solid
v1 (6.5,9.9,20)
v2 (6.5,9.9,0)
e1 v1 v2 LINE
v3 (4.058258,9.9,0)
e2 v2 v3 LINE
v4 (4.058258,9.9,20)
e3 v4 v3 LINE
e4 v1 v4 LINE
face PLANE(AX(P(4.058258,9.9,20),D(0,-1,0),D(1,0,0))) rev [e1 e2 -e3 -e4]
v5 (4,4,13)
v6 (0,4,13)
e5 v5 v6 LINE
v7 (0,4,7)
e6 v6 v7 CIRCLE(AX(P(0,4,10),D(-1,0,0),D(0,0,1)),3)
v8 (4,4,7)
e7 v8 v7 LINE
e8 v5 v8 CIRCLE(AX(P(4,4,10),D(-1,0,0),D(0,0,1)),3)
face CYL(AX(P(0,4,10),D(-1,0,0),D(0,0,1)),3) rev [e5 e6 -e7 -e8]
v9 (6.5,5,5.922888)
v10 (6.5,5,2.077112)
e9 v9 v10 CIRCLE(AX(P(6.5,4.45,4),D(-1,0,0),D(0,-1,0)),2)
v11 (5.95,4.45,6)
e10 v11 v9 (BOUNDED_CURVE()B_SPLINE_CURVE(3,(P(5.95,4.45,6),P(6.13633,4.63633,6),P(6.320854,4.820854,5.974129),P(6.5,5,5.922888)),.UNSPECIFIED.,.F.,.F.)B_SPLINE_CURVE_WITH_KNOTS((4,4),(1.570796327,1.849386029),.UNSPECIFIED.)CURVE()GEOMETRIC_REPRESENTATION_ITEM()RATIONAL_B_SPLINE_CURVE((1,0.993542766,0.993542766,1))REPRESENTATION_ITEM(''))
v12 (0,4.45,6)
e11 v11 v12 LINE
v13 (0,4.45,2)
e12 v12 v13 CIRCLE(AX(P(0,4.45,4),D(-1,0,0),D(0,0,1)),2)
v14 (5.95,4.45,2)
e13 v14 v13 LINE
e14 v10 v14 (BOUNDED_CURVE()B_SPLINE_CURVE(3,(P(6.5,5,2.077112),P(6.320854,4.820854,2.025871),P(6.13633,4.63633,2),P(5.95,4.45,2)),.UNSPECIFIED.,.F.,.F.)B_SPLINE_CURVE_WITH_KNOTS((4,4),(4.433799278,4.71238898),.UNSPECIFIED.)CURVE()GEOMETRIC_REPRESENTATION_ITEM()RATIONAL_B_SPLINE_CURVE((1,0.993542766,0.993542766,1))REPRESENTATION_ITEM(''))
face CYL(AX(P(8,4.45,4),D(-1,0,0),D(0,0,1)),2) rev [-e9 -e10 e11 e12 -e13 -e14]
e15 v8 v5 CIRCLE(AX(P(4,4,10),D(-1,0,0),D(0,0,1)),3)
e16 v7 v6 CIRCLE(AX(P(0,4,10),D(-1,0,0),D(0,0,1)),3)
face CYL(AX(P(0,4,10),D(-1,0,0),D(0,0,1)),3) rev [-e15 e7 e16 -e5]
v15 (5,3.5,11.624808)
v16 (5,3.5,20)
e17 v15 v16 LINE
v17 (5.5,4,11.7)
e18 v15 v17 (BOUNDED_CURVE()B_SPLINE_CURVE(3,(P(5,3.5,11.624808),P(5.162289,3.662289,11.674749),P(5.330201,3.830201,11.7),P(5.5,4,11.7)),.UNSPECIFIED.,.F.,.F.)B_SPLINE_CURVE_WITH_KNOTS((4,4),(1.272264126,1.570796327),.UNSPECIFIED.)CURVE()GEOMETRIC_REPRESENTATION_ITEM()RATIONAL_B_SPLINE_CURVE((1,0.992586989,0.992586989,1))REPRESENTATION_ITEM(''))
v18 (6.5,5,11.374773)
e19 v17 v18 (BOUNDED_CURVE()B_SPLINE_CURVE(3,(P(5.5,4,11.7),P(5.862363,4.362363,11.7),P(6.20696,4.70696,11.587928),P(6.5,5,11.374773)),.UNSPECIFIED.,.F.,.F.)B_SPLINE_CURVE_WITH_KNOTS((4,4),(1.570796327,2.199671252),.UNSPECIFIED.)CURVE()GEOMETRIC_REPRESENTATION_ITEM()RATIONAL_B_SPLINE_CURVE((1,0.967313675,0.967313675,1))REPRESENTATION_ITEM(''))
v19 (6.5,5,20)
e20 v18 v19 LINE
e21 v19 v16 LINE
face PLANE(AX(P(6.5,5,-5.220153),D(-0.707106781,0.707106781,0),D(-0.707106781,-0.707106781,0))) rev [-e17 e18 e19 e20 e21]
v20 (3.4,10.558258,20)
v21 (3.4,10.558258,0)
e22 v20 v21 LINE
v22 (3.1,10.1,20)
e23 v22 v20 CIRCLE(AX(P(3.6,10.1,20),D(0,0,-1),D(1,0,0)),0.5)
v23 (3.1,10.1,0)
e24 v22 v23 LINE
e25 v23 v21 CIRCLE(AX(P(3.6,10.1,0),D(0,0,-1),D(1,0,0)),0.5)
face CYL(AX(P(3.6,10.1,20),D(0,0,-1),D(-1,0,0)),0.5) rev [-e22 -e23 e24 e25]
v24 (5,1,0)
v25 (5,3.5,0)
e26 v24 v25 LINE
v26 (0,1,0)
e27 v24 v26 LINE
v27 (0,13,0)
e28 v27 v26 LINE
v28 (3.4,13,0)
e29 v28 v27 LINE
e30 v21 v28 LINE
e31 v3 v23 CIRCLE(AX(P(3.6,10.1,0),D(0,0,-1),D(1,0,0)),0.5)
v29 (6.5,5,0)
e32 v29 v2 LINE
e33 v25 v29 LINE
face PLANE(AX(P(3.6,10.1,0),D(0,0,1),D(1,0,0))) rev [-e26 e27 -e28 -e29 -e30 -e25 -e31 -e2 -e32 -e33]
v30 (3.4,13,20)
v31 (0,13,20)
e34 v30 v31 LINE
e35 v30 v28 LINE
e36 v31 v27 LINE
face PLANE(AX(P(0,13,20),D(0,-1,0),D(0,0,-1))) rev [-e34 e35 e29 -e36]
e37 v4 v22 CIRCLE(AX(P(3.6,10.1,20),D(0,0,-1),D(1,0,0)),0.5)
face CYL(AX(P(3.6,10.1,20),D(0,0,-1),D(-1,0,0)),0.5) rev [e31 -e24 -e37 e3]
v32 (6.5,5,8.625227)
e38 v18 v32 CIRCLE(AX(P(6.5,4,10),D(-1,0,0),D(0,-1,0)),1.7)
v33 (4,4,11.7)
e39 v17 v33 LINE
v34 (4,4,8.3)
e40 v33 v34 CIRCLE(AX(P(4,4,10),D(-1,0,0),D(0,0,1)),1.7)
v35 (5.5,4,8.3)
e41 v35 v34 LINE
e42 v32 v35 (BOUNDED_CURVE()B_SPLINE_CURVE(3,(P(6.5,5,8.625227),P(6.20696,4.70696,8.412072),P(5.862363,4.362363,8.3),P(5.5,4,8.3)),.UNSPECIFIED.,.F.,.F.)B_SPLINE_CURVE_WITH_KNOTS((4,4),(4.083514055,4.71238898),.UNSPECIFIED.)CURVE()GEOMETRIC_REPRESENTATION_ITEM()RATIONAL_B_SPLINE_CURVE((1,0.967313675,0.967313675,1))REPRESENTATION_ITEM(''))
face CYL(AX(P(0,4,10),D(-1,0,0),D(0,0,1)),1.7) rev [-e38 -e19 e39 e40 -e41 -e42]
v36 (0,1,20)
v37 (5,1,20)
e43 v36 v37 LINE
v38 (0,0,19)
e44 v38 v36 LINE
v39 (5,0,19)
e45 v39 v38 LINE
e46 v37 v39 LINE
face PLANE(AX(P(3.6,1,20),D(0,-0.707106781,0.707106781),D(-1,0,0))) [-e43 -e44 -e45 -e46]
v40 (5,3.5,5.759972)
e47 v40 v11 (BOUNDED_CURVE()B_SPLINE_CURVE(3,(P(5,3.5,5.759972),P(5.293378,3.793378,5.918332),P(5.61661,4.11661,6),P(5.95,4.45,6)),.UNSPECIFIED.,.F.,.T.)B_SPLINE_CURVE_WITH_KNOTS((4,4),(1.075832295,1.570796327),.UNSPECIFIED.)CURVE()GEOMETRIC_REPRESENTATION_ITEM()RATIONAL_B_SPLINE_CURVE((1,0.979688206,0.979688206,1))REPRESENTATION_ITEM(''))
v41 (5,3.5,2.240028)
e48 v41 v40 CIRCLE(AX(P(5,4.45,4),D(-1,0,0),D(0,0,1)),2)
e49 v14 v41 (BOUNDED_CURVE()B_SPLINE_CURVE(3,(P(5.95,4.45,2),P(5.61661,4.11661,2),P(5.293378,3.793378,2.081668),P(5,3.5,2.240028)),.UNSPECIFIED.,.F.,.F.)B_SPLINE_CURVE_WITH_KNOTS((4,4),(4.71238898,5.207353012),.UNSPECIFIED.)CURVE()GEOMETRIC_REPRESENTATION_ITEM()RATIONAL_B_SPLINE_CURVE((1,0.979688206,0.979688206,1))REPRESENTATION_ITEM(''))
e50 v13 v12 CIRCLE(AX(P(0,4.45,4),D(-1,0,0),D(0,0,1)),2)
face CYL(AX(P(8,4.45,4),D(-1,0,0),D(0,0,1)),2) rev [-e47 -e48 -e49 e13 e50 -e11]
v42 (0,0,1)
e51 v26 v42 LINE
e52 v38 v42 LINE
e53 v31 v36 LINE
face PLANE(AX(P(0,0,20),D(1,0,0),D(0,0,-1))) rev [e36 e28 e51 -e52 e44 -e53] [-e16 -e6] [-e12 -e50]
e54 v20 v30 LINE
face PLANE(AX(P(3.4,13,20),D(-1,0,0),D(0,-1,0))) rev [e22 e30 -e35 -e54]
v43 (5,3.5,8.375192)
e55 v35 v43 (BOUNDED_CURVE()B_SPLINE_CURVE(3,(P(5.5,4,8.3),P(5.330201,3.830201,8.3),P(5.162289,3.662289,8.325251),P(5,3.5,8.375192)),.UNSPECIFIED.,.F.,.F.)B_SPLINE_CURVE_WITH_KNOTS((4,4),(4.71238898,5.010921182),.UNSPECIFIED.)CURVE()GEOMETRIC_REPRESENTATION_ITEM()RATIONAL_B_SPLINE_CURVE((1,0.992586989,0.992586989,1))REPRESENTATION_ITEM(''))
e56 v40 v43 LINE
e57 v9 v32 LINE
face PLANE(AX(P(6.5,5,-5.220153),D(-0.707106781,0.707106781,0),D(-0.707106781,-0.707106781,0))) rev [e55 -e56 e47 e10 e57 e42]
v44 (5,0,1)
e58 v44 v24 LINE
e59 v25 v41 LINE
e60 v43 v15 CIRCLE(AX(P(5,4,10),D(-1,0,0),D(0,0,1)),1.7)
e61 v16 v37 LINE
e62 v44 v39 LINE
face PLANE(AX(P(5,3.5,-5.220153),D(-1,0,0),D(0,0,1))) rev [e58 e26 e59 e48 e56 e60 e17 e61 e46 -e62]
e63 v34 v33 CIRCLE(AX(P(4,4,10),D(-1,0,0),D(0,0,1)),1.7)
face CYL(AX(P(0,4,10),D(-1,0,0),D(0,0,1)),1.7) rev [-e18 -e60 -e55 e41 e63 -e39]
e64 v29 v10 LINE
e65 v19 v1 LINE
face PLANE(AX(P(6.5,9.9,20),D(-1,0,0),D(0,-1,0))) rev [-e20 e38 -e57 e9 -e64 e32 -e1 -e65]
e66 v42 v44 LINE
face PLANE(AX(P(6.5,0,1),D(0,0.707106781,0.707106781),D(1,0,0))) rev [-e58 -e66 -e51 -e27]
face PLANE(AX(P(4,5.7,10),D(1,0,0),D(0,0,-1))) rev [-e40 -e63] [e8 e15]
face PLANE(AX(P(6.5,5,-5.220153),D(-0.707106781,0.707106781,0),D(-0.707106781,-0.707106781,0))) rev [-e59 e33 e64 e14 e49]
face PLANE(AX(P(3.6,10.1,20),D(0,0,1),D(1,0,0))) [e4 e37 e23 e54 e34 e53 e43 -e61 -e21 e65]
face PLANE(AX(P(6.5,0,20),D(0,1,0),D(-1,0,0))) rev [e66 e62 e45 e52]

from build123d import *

# Parameters (mm, degrees)
BOSS_EXTRUDE1_DEPTH                                  = 20
CUT_EXTRUDE1_DEPTH                                   = 20
HOLE_SIZE_PER_SOCKET_HEAD_CAP_SCREW_TYPE_D           = 3.4
HOLE_SIZE_PER_SOCKET_HEAD_CAP_SCREW_TYPE_DEPTH       = 10
HOLE_SIZE_PER_SOCKET_HEAD_CAP_SCREW_TYPE_CBORE_D     = 6
HOLE_SIZE_PER_SOCKET_HEAD_CAP_SCREW_TYPE_CBORE_DEPTH = 4
HOLE_SIZE_PER_SOCKET_HEAD_CAP_SCREW_TYPE_TIP         = 1.021463052
CHAMFER1_SIZE                                        = 1
SKETCH8_R                                            = 2
CUT_EXTRUDE2_DEPTH                                   = 8


with BuildPart() as part:
    # Sketch1 → Boss-Extrude1 (new body)
    with BuildSketch(Plane.XY):
        with BuildLine():
            Line((0, 0), (0, 13))
            Line((0, 13), (3.4, 13))
            Line((3.4, 13), (3.4, 10.558257569))
            ThreePointArc((3.4, 10.558257569), (3.246446609, 9.746446609), (4.058257569, 9.9))
            Line((4.058257569, 9.9), (6.5, 9.9))
            Line((6.5, 9.9), (6.5, 0))
            Line((6.5, 0), (0, 0))
        make_face()
    extrude(amount=BOSS_EXTRUDE1_DEPTH)

    # Sketch7 → Cut-Extrude1 (cut)
    with BuildSketch(Plane.XY.offset(20)):
        Polygon((6.5, 5), (5, 3.5), (5, 0), (6.5, 0), align=None)
    extrude(amount=-CUT_EXTRUDE1_DEPTH, mode=Mode.SUBTRACT)

    # Hole size per socket head cap screw type 0
    with Locations(Plane(origin=(0, 0, 0), x_dir=(0, 0, -1), z_dir=(-1, 0, 0))):
        with Locations((-10, -4)):
            CounterBoreHole(HOLE_SIZE_PER_SOCKET_HEAD_CAP_SCREW_TYPE_D / 2, HOLE_SIZE_PER_SOCKET_HEAD_CAP_SCREW_TYPE_CBORE_D / 2, HOLE_SIZE_PER_SOCKET_HEAD_CAP_SCREW_TYPE_CBORE_DEPTH, depth=HOLE_SIZE_PER_SOCKET_HEAD_CAP_SCREW_TYPE_DEPTH)
            with Locations((0, 0, -(HOLE_SIZE_PER_SOCKET_HEAD_CAP_SCREW_TYPE_DEPTH + HOLE_SIZE_PER_SOCKET_HEAD_CAP_SCREW_TYPE_TIP / 2))):  # 118° drill point
                Cone(0, HOLE_SIZE_PER_SOCKET_HEAD_CAP_SCREW_TYPE_D / 2, HOLE_SIZE_PER_SOCKET_HEAD_CAP_SCREW_TYPE_TIP, mode=Mode.SUBTRACT)

    # Chamfer1
    chamfer1_edges = [part.edges().sort_by_distance(p)[0] for p in [
        (2.5, 0, 20),
        (2.5, 0, 0),
    ]]
    chamfer(chamfer1_edges, length=CHAMFER1_SIZE)

    # Sketch8 → Cut-Extrude2 (cut)
    with BuildSketch(Plane.ZY):
        with Locations((4, 4.45)):
            Circle(SKETCH8_R)
    extrude(amount=-CUT_EXTRUDE2_DEPTH, mode=Mode.SUBTRACT)


solid = part.part
